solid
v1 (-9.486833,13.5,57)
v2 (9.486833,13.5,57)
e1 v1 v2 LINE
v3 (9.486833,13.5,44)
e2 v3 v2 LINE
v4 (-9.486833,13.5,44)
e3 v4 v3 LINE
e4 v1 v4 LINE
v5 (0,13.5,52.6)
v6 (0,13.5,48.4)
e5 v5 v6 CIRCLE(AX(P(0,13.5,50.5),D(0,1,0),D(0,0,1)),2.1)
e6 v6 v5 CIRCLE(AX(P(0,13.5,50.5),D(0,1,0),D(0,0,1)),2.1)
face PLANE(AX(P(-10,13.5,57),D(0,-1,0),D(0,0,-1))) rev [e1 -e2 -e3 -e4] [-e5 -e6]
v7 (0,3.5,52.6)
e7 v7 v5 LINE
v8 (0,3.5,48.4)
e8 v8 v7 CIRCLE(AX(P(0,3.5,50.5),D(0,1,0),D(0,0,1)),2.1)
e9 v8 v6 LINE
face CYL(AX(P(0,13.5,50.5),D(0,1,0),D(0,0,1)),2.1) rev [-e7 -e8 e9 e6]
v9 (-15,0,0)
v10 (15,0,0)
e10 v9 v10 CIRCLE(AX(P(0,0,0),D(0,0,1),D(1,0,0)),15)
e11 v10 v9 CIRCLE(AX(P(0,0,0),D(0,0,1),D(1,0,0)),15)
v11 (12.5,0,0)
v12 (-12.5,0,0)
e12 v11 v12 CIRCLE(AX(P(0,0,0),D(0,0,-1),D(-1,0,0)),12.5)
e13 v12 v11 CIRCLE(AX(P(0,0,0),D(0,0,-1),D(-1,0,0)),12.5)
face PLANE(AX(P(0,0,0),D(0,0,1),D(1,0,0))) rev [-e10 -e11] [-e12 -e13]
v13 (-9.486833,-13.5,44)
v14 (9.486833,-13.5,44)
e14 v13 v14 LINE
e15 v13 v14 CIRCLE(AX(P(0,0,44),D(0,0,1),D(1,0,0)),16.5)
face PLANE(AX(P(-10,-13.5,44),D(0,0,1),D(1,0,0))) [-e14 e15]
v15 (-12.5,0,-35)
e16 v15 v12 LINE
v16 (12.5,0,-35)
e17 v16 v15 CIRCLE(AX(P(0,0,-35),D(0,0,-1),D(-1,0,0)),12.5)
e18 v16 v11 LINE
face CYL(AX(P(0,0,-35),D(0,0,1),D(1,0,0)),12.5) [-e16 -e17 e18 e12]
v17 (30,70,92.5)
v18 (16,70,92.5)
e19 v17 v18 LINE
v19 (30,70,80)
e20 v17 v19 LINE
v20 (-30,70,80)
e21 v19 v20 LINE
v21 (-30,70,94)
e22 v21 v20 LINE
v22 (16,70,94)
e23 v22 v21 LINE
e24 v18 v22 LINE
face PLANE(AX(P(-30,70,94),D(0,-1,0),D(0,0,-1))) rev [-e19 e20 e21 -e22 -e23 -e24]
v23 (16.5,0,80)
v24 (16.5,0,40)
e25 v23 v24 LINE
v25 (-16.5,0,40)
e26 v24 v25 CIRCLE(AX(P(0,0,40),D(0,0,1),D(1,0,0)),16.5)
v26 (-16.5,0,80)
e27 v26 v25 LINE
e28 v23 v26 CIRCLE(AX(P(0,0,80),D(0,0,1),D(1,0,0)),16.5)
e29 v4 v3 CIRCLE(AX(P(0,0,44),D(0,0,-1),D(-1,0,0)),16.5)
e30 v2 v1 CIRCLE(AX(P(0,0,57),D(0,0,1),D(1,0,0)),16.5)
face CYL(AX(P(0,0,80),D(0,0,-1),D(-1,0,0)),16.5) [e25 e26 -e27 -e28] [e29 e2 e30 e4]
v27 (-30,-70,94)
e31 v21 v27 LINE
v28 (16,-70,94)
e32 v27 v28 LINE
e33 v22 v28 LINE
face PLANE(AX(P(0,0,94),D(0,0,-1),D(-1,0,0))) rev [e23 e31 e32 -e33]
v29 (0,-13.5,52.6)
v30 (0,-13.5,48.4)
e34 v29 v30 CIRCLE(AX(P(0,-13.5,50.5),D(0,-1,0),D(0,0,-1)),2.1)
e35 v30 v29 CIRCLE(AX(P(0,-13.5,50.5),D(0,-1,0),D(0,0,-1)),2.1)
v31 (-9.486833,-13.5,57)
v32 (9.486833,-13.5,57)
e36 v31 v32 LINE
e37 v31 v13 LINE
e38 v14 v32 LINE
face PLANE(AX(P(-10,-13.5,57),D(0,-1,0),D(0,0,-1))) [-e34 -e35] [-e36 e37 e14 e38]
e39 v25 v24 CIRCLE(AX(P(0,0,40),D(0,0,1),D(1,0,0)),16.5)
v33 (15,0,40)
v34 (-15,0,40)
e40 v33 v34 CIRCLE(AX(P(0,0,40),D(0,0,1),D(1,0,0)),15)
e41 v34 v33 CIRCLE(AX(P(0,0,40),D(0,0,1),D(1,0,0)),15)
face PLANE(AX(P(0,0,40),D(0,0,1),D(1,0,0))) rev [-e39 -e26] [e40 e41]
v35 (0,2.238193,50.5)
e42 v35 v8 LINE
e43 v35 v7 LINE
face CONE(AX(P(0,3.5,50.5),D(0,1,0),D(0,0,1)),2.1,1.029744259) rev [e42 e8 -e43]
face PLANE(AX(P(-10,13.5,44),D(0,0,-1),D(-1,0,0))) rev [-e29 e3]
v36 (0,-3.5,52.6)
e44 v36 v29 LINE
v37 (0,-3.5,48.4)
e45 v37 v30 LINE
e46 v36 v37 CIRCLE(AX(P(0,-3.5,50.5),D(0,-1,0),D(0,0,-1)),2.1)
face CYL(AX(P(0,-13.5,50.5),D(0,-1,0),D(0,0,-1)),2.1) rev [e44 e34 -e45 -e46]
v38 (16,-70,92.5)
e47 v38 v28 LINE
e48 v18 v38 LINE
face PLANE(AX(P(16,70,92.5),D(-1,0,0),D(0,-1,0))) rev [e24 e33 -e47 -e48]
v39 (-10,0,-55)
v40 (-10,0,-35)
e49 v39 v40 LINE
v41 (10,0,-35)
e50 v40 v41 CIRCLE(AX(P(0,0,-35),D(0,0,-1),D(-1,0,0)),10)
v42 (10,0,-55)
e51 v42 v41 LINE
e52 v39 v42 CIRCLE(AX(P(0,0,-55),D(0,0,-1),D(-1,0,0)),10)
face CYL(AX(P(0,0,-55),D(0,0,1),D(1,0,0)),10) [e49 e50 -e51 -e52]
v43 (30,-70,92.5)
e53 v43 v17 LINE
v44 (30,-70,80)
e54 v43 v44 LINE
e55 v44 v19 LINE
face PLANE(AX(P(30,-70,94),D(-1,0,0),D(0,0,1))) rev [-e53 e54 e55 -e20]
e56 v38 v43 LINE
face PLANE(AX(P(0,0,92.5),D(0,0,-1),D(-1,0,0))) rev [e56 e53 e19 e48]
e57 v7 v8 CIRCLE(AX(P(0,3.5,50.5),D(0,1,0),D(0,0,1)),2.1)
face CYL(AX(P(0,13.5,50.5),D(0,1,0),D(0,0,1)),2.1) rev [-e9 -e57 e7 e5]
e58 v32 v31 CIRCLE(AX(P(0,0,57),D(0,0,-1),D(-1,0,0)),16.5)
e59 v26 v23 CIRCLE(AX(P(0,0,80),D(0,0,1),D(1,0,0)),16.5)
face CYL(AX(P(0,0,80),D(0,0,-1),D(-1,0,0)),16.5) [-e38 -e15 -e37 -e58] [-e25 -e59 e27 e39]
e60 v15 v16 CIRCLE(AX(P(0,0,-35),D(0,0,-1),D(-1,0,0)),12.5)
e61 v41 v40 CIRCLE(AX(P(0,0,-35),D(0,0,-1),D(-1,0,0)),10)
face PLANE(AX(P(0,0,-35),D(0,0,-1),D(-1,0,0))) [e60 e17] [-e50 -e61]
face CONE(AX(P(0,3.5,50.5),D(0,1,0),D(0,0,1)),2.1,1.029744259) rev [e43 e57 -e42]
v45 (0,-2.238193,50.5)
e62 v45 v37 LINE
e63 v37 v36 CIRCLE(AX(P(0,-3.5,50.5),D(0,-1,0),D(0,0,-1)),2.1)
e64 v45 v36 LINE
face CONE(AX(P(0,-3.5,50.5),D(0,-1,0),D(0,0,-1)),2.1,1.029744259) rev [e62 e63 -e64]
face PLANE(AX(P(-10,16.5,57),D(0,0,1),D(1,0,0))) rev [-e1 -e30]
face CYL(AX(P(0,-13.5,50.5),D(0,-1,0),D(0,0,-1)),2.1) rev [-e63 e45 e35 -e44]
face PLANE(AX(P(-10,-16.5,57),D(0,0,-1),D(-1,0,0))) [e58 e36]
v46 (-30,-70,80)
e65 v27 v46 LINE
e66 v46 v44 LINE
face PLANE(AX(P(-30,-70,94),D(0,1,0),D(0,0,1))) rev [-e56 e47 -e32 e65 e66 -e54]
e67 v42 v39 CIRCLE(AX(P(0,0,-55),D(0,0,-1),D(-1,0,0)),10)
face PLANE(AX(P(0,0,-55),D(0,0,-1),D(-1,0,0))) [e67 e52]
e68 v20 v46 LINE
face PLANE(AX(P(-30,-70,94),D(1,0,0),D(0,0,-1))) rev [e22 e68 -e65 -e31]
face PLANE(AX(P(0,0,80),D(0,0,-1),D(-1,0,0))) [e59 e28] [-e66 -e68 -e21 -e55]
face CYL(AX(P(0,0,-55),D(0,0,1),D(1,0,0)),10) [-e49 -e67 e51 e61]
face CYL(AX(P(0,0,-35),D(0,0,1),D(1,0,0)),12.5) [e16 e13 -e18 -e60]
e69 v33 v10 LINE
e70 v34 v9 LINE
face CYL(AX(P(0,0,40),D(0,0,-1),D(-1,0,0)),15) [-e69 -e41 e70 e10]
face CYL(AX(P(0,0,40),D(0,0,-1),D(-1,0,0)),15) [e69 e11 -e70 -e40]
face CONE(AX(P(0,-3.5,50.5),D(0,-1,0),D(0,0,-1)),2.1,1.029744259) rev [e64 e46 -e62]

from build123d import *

# Parameters (mm, degrees)
SKETCH_1_R          = 15
EXTRUDE_1_DEPTH     = 40
SKETCH_2_R          = 16.5
EXTRUDE_2_DEPTH     = 40
SKETCH_3_R          = 12.5
EXTRUDE_3_DEPTH     = 35
SKETCH_4_R          = 10
EXTRUDE_4_DEPTH     = 20
SKETCH_5_W          = 60
SKETCH_5_H          = 140
EXTRUDE_5_DEPTH     = 14
SKETCH_6_W          = 14
SKETCH_6_H          = 140
CUT_EXTRUDE_1_DEPTH = 1.5
SKETCH_7_W          = 13
SKETCH_7_H          = 3
CUT_EXTRUDE_2_DEPTH = 10


with BuildPart() as part:
    # 草图1 → 凸台-拉伸1 (new body)
    with BuildSketch(Plane.XY):
        Circle(SKETCH_1_R)
    extrude(amount=EXTRUDE_1_DEPTH)

    # 草图2 → 凸台-拉伸2 (add)
    with BuildSketch(Plane.XY.offset(40)):
        Circle(SKETCH_2_R)
    extrude(amount=EXTRUDE_2_DEPTH)

    # 草图3 → 凸台-拉伸3 (add)
    with BuildSketch(Plane(origin=(0, 0, 0), x_dir=(-1, 0, 0), z_dir=(0, 0, -1))):
        Circle(SKETCH_3_R)
    extrude(amount=EXTRUDE_3_DEPTH)

    # 草图4 → 凸台-拉伸4 (add)
    with BuildSketch(Plane(origin=(0, 0, -35), x_dir=(-1, 0, 0), z_dir=(0, 0, -1))):
        Circle(SKETCH_4_R)
    extrude(amount=EXTRUDE_4_DEPTH)

    # 草图5 → 凸台-拉伸5 (add)
    with BuildSketch(Plane.XY.offset(80)):
        Rectangle(SKETCH_5_W, SKETCH_5_H)
    extrude(amount=EXTRUDE_5_DEPTH)

    # 草图6 → 切除-拉伸1 (cut)
    with BuildSketch(Plane.XY.offset(94)):
        with Locations((23, 0)):
            Rectangle(SKETCH_6_W, SKETCH_6_H)
    extrude(amount=-CUT_EXTRUDE_1_DEPTH, mode=Mode.SUBTRACT)

    # 草图7 → 切除-拉伸2 (cut, symmetric)
    with BuildSketch(Plane(origin=(0, 0, 0), x_dir=(0, 0, -1), z_dir=(1, 0, 0))):
        with Locations((-50.5, 15)):
            Rectangle(SKETCH_7_W, SKETCH_7_H)
    cut_extrude_2 = extrude(amount=CUT_EXTRUDE_2_DEPTH, both=True, mode=Mode.SUBTRACT)

    # 镜向1: 切除-拉伸2 across plane
    add(cut_extrude_2.mirror(Plane.ZX), mode=Mode.SUBTRACT)

    # 草图8 → M5 螺纹孔1 (revolve, cut)
    with BuildSketch(Plane(origin=(0, 13.5, 50.5), x_dir=(0, 0, 1), z_dir=(1, 0, 0))):
        Polygon((0, 0), (0, 11.2618073), (2.1, 10), (2.1, 0), align=None)
    hole_wizard_m5_1 = revolve(axis=Axis((0, 19.85, 50.5), (0, -1, 0)), mode=Mode.SUBTRACT)

    # 镜向2: M5 螺纹孔1 across plane
    add(hole_wizard_m5_1.mirror(Plane.ZX), mode=Mode.SUBTRACT)


solid = part.part
